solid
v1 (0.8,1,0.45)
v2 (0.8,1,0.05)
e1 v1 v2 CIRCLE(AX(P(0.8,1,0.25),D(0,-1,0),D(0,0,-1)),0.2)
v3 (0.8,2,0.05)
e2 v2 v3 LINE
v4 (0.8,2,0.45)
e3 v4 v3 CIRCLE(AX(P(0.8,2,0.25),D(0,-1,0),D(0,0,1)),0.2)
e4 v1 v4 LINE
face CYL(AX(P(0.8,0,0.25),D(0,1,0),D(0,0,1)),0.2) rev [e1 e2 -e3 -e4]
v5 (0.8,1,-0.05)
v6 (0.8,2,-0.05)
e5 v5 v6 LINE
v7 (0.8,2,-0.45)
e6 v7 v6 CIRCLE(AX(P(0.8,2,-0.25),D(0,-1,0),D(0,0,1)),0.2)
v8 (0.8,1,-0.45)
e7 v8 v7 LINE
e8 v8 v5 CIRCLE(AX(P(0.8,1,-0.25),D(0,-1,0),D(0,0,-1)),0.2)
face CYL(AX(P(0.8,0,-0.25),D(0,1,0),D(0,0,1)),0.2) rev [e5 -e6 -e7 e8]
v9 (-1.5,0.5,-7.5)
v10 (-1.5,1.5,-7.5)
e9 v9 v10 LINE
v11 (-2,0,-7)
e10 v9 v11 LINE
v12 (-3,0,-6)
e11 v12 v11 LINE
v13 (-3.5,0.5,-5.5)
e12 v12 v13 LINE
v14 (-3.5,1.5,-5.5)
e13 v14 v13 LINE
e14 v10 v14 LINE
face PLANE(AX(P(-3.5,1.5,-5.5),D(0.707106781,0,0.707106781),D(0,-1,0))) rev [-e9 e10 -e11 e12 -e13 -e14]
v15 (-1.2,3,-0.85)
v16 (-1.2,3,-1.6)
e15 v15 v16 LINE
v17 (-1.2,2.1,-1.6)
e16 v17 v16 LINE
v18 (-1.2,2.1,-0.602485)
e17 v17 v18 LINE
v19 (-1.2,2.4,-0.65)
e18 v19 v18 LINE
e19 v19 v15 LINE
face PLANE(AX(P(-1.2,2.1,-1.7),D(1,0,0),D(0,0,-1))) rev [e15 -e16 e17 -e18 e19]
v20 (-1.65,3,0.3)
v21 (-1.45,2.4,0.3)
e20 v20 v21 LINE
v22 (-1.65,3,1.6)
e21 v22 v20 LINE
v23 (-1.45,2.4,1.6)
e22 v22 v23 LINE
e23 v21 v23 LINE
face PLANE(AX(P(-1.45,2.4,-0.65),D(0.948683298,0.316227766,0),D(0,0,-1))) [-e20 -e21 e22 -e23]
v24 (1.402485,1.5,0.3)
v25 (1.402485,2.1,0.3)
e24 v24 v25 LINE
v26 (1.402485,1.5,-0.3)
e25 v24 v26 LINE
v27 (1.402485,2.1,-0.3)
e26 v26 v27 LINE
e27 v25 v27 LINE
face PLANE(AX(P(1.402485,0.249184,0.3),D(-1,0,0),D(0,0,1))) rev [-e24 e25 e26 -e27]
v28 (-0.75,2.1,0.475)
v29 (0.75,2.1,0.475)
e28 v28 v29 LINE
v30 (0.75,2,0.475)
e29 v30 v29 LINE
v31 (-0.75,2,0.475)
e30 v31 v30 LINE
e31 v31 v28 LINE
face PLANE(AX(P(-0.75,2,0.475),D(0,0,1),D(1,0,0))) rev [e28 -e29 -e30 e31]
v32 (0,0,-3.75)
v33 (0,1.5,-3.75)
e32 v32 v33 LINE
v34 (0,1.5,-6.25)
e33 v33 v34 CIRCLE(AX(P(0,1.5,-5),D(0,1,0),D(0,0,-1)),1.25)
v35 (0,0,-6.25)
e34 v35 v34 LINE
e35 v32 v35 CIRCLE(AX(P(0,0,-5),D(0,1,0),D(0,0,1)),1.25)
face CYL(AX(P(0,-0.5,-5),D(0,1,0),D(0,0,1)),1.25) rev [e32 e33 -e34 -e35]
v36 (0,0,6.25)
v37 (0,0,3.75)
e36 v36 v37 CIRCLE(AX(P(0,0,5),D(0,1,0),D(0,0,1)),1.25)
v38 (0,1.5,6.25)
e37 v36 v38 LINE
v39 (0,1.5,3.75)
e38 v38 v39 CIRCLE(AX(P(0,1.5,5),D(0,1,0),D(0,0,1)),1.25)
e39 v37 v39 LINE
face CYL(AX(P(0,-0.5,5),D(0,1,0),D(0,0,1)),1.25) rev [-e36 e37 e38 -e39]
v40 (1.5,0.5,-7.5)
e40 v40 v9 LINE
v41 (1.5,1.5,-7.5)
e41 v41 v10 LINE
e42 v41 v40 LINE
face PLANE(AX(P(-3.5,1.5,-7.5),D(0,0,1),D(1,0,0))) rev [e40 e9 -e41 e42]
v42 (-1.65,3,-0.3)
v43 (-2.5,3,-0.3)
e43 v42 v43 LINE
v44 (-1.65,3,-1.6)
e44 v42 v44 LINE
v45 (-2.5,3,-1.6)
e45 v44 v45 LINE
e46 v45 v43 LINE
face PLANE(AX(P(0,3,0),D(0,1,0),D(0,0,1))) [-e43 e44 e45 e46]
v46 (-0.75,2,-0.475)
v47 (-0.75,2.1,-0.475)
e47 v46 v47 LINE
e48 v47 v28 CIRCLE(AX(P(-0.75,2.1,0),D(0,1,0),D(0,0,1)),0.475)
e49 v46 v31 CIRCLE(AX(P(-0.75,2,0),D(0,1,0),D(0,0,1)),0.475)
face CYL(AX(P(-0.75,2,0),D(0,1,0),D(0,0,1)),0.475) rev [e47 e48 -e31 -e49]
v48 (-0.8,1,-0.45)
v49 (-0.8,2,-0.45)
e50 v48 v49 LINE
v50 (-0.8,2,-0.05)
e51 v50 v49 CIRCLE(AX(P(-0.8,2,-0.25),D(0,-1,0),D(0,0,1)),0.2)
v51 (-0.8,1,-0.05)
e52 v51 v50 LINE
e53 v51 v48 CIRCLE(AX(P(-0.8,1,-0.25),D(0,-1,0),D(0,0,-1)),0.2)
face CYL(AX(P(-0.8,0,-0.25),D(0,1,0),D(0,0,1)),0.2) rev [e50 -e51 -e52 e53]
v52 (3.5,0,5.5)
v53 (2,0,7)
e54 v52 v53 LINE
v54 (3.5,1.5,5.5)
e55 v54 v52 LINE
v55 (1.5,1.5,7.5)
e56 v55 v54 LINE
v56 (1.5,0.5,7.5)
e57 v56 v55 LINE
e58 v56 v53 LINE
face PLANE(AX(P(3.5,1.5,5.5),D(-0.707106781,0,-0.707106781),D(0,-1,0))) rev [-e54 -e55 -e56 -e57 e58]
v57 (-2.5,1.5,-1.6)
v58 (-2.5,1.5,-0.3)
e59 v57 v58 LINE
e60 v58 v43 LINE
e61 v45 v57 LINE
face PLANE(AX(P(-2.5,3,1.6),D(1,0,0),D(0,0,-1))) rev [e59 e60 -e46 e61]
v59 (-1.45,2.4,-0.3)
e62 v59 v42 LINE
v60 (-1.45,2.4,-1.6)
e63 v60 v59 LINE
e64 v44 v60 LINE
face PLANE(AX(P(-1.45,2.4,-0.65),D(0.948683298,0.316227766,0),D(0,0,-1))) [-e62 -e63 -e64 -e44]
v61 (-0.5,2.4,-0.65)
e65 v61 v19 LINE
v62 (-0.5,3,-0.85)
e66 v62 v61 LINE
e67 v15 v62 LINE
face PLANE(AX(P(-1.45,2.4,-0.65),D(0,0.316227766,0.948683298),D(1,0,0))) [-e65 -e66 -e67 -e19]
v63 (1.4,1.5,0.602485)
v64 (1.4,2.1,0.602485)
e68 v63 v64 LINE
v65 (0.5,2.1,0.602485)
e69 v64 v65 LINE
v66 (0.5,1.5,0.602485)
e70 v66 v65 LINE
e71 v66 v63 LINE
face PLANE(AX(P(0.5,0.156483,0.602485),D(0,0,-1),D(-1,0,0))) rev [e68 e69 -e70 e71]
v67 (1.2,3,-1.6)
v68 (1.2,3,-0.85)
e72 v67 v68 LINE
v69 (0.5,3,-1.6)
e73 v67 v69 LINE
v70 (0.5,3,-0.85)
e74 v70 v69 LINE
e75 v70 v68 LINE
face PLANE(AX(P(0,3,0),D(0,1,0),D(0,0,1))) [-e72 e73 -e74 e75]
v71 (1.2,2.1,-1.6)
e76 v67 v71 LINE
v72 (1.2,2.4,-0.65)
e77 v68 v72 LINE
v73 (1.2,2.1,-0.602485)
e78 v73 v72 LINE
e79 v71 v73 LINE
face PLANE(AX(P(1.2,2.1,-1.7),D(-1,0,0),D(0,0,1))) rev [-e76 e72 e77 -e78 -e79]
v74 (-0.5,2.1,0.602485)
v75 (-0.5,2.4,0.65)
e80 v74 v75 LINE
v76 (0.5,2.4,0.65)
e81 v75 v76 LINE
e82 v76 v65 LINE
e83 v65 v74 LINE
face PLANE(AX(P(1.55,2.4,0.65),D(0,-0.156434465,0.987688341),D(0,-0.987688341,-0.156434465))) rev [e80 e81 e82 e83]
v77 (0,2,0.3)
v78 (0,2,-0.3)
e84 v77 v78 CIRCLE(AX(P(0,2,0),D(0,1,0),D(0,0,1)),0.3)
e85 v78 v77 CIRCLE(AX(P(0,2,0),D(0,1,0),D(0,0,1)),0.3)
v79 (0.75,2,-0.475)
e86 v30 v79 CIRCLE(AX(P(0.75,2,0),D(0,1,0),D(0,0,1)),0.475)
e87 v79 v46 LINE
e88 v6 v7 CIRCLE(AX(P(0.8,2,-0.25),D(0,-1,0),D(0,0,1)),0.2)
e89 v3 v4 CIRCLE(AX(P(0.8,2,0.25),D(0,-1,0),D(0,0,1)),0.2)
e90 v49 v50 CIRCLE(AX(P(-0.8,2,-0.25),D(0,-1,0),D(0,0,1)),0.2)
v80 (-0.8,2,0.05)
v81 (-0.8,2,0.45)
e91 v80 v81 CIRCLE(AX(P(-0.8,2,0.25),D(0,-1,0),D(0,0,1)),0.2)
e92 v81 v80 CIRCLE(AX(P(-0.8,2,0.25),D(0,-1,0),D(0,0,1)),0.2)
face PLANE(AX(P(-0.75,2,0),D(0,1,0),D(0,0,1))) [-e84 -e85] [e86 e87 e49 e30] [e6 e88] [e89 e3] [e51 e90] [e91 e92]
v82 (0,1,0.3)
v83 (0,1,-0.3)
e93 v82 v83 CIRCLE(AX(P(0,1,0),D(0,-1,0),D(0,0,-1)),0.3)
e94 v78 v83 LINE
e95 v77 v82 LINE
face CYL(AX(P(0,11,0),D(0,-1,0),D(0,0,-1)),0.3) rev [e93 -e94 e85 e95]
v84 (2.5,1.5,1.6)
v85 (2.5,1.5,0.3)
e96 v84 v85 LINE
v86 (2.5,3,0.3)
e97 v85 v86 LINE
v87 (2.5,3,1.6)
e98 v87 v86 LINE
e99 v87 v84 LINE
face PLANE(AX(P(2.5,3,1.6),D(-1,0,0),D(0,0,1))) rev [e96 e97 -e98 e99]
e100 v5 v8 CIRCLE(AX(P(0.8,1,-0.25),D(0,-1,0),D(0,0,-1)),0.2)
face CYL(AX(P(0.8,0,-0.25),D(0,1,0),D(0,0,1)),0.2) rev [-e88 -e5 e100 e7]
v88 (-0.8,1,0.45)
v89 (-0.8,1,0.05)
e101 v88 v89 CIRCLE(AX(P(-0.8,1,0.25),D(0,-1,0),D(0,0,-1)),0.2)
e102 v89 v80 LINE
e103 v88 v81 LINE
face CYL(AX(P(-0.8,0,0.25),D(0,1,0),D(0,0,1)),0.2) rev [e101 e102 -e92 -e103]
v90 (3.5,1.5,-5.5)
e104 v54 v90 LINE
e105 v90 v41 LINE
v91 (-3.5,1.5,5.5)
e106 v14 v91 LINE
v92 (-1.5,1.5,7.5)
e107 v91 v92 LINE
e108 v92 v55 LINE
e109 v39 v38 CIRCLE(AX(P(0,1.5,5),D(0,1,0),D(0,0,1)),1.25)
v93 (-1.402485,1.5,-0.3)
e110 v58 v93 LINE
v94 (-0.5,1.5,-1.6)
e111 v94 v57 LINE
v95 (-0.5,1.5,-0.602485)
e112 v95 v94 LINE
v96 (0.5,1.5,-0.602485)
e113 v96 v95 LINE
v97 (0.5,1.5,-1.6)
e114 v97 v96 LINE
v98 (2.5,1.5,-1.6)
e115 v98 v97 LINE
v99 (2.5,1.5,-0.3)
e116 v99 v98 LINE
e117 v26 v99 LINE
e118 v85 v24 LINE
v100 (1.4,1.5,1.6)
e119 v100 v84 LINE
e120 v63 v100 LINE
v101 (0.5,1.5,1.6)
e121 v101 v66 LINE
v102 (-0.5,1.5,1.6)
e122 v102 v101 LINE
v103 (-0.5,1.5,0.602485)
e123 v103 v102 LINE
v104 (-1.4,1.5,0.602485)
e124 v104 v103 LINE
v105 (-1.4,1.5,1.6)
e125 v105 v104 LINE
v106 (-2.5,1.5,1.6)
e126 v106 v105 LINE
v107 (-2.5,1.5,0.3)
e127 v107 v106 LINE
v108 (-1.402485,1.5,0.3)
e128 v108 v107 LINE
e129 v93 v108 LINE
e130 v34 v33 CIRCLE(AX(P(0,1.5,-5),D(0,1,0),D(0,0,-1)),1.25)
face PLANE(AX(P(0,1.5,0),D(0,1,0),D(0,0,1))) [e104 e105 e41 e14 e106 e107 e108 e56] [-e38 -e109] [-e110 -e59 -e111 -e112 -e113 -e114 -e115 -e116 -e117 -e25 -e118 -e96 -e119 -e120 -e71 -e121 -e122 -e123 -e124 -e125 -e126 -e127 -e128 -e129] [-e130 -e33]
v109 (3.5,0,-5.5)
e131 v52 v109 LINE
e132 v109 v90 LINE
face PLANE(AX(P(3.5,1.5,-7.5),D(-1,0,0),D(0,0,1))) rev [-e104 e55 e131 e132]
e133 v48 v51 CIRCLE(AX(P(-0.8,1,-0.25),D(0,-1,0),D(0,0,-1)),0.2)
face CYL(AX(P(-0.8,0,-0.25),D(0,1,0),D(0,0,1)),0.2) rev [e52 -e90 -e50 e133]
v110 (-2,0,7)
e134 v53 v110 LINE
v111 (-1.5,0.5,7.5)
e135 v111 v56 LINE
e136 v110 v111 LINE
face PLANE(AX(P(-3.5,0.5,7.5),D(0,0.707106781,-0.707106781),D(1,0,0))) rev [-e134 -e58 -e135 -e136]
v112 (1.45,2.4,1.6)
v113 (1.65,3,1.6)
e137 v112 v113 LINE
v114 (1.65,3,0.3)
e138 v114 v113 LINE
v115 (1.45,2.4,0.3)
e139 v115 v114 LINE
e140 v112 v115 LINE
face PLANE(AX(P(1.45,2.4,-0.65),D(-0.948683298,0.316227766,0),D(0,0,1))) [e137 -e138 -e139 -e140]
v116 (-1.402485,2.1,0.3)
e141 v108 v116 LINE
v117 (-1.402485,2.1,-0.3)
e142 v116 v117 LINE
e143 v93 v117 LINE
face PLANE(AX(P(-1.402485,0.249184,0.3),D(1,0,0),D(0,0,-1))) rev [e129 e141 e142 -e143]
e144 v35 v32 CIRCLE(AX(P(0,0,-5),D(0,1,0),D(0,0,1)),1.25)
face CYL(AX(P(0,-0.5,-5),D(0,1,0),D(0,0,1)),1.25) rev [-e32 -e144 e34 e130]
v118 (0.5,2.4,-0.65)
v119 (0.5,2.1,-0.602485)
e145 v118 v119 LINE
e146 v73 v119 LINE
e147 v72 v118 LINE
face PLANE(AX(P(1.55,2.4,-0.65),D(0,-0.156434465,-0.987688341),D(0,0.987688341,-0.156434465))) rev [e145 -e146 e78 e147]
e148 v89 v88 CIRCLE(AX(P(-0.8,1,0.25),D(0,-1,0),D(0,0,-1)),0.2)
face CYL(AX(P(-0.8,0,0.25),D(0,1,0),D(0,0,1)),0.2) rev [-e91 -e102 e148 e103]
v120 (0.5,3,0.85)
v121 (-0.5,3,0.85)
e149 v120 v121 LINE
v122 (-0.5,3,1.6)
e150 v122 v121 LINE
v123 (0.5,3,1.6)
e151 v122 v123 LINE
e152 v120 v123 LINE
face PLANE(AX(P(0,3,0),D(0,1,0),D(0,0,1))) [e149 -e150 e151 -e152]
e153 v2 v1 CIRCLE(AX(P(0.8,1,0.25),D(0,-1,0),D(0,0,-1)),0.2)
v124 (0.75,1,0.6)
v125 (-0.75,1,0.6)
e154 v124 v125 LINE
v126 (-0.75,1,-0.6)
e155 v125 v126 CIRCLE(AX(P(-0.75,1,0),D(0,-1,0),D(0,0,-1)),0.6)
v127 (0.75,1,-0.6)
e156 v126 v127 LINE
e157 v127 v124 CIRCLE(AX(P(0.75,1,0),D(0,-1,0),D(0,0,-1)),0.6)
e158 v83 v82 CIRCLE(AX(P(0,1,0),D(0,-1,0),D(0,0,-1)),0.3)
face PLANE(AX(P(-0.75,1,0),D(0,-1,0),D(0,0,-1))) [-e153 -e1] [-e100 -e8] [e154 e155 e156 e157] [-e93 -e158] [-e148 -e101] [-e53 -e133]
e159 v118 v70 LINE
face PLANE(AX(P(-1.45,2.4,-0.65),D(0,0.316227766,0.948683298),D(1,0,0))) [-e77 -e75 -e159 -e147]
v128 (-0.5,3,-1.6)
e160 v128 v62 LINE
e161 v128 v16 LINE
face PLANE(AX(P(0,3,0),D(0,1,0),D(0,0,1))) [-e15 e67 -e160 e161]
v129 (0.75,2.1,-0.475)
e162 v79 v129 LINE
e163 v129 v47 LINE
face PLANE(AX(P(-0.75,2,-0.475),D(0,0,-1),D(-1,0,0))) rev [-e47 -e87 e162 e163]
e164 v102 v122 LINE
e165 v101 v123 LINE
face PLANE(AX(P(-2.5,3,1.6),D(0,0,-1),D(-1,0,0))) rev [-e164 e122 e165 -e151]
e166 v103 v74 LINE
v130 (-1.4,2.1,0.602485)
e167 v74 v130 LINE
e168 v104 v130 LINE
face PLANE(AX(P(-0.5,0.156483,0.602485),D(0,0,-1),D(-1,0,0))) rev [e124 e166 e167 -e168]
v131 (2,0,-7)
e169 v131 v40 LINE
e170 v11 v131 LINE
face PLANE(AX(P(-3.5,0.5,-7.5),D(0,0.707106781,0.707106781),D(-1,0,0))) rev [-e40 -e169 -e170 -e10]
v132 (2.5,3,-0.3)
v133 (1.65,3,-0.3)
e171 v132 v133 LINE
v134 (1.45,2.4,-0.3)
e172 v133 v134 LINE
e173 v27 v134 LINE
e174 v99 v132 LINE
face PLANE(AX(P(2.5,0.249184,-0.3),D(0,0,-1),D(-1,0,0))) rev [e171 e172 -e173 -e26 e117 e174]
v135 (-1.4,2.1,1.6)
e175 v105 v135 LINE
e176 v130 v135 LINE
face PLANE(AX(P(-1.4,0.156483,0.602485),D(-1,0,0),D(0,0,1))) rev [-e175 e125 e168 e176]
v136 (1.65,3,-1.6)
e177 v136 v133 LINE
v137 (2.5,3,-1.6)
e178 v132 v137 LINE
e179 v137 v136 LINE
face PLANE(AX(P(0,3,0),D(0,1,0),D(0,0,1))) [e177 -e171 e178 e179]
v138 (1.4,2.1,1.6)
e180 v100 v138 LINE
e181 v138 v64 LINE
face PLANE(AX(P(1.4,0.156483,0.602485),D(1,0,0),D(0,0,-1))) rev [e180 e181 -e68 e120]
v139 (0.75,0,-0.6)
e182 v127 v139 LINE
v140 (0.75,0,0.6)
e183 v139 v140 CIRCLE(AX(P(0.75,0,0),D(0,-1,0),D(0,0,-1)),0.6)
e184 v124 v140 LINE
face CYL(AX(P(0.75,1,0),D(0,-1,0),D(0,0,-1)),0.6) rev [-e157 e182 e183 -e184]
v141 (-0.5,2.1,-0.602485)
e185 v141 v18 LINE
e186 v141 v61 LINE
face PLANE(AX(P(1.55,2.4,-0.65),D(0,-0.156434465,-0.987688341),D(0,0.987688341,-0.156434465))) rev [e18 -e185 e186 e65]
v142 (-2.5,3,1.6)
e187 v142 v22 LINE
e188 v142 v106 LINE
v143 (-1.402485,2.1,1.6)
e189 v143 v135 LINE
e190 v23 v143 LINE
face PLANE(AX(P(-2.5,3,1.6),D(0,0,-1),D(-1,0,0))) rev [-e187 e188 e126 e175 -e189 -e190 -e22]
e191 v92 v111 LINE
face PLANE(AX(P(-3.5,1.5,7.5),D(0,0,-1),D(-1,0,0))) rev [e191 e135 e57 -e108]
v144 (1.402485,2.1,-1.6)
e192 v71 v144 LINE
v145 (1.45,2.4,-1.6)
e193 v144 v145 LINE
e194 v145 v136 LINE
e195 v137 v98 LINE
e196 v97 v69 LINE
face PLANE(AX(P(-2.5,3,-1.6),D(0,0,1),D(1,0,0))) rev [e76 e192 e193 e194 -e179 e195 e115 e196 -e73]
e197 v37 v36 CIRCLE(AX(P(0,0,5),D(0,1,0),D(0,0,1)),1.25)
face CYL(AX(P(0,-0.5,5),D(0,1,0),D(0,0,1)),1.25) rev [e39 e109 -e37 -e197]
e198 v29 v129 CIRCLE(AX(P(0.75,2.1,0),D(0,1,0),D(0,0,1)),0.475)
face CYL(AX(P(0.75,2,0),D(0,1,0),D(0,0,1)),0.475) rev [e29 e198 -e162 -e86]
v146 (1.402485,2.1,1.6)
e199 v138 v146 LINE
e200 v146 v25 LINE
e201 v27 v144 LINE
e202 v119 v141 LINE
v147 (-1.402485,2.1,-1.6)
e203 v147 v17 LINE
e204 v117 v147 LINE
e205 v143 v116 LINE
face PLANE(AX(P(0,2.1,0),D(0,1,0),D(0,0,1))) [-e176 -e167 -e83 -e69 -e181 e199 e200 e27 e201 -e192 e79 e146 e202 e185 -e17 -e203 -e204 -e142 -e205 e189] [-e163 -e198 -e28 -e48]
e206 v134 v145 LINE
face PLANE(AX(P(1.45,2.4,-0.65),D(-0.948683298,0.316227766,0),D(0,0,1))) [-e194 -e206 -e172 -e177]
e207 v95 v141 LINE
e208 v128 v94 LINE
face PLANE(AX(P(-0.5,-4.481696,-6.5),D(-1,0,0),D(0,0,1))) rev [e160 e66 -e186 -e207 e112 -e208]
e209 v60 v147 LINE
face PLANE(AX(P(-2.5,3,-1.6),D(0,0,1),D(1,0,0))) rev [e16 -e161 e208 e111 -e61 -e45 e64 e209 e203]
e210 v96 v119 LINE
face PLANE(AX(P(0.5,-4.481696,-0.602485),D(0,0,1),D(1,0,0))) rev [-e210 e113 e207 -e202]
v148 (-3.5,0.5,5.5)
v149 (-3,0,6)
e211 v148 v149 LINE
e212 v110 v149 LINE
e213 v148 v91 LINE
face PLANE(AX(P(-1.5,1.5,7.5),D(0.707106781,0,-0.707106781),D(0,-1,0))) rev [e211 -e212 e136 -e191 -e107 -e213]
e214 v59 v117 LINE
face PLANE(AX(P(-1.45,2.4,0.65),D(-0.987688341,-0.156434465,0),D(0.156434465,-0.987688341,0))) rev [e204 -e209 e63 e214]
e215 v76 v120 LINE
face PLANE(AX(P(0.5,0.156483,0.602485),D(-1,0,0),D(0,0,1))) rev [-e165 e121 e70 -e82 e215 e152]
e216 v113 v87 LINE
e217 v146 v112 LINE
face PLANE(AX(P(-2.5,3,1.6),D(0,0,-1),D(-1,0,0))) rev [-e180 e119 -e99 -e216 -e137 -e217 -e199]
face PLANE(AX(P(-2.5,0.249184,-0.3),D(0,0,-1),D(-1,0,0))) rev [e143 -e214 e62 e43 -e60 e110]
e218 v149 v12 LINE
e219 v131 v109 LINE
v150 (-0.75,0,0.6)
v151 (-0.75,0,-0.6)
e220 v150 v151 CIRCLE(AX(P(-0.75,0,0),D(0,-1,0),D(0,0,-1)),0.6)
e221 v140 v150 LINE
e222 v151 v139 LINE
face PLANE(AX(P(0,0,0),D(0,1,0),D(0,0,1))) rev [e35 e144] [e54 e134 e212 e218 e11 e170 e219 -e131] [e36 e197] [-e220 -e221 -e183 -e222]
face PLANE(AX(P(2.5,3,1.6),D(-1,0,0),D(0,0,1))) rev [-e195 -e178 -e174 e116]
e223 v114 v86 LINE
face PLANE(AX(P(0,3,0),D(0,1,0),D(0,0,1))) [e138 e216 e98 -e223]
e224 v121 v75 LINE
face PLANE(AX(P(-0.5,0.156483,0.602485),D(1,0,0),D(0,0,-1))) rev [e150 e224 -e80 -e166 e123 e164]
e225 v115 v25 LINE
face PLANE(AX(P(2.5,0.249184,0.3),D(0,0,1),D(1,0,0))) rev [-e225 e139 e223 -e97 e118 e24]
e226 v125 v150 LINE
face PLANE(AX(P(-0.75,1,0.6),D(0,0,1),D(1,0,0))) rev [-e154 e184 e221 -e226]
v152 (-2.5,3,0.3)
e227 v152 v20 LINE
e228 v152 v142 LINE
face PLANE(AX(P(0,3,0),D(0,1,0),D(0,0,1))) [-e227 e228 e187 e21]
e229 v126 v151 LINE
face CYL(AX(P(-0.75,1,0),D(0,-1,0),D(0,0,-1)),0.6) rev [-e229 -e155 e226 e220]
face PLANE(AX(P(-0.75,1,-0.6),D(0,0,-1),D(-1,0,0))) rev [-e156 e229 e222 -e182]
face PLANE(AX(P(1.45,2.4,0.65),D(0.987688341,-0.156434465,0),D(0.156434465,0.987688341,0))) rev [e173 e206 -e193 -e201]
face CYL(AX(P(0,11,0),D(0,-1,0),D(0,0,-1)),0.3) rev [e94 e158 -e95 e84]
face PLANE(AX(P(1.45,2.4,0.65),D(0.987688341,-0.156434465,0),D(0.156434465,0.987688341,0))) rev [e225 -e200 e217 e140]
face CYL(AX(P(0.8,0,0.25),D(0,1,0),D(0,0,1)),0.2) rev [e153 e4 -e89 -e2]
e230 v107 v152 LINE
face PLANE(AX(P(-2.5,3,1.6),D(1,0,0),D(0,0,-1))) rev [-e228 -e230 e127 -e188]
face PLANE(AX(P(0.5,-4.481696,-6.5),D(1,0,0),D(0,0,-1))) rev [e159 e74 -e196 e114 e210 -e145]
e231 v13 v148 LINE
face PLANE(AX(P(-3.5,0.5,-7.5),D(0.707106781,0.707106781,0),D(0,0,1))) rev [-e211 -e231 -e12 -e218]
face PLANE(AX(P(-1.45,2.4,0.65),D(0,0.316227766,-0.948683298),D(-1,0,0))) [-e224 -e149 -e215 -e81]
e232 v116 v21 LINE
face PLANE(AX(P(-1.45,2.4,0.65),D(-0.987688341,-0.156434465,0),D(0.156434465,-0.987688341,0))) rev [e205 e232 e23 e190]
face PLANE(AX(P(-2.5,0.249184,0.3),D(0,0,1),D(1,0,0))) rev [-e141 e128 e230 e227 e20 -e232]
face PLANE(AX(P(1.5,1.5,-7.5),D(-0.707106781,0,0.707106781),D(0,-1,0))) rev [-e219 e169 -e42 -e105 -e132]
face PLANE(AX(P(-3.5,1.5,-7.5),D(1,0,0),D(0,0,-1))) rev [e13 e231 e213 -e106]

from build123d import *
from OCP.BRepFilletAPI import BRepFilletAPI_MakeChamfer

# Parameters (mm, degrees)
SKETCH1_W           = 7
SKETCH1_H           = 15
BOSS_EXTRUDE1_DEPTH = 1.5
SKETCH2_W           = 5
SKETCH2_H           = 3.2
BOSS_EXTRUDE2_DEPTH = 1.5
SKETCH3_W           = 2.9
SKETCH3_H           = 1.3
CUT_EXTRUDE1_DEPTH  = 0.9
CUT_EXTRUDE2_DEPTH  = 1
CHAMFER1_SIZE       = 0.2
CHAMFER1_SIZE2      = 0.6
CHAMFER2_SIZE       = 0.2
CHAMFER2_SIZE2      = 0.6
CHAMFER3_SIZE       = 2
SKETCH8_R           = 1.25
CUT_EXTRUDE6_DEPTH  = 2
SKETCH9_R           = 0.2
CUT_EXTRUDE7_DEPTH  = 9.538735269
CUT_EXTRUDE8_DEPTH  = 0.1
BOSS_EXTRUDE3_DEPTH = 1.55
BOSS_EXTRUDE4_DEPTH = 0.65
CUT_EXTRUDE3_REACH  = 10.803
SKETCH5_W           = 1
SKETCH5_H           = 5.897515332
CUT_EXTRUDE4_REACH  = 10.803
SKETCH6_W           = 1.097515332
SKETCH6_H           = 0.6
CUT_EXTRUDE5_REACH  = 10.803
SKETCH7_W           = 0.9
SKETCH7_H           = 0.997515332
CHAMFER5_SIZE       = 0.25
CHAMFER5_SIZE2      = 0.6
CUT_EXTRUDE9_DEPTH  = 1.3
CUT_EXTRUDE10_DEPTH = 3.3
SKETCH19_R          = 0.3
CUT_EXTRUDE11_DEPTH = 10
CHAMFER6_SIZE       = 0.5


with BuildPart() as part:
    # Sketch1 → Boss-Extrude1 (new body)
    with BuildSketch(Plane(origin=(0, 0, 0), x_dir=(1, 0, 0), z_dir=(0, 1, 0))):
        Rectangle(SKETCH1_W, SKETCH1_H)
    extrude(amount=BOSS_EXTRUDE1_DEPTH)

    # Sketch2 → Boss-Extrude2 (add)
    with BuildSketch(Plane(origin=(0, 1.5, 0), x_dir=(1, 0, 0), z_dir=(0, 1, 0))):
        Rectangle(SKETCH2_W, SKETCH2_H)
    extrude(amount=BOSS_EXTRUDE2_DEPTH)

    # Sketch3 → Cut-Extrude1 (cut)
    with BuildSketch(Plane(origin=(0, 3, 0), x_dir=(1, 0, 0), z_dir=(0, 1, 0))):
        Rectangle(SKETCH3_W, SKETCH3_H)
    extrude(amount=-CUT_EXTRUDE1_DEPTH, mode=Mode.SUBTRACT)

    # Sketch4 → Cut-Extrude2 (cut)
    with BuildSketch(Plane.XZ):
        with BuildLine():
            Line((-0.75, 0.6), (0.75, 0.6))
            ThreePointArc((0.75, 0.6), (1.35, 0), (0.75, -0.6))
            Line((0.75, -0.6), (-0.75, -0.6))
            ThreePointArc((-0.75, -0.6), (-1.35, 0), (-0.75, 0.6))
        make_face()
    extrude(amount=-CUT_EXTRUDE2_DEPTH, mode=Mode.SUBTRACT)

    # Chamfer1
    chamfer1_edges = [part.edges().sort_by_distance(p)[0] for p in [
        (0, 3, -0.65),
        (0, 3, 0.65),
    ]]
    chamfer1_side = [part.faces().sort_by_distance(p)[0] for p in [
        (-2.440636712, 3, 0),
    ]]
    chamfer(chamfer1_edges, length=CHAMFER1_SIZE, length2=CHAMFER1_SIZE2, reference=chamfer1_side[0])

    # Chamfer2
    chamfer2_edges = [part.edges().sort_by_distance(p)[0] for p in [
        (-1.45, 3, 0),
        (1.45, 3, 0),
    ]]
    chamfer2_side = [part.faces().sort_by_distance(p)[0] for p in [
        (0, 3, -0.909363288),
    ]]
    chamfer(chamfer2_edges, length=CHAMFER2_SIZE, length2=CHAMFER2_SIZE2, reference=chamfer2_side[0])

    # Chamfer3
    chamfer3_edges = [part.edges().sort_by_distance(p)[0] for p in [
        (3.5, 0.75, 7.5),
        (-3.5, 0.75, 7.5),
        (-3.5, 0.75, -7.5),
        (3.5, 0.75, -7.5),
    ]]
    chamfer(chamfer3_edges, length=CHAMFER3_SIZE)

    # Sketch8 → Cut-Extrude6 (cut)
    with BuildSketch(Plane(origin=(0, 1.5, 0), x_dir=(1, 0, 0), z_dir=(0, 1, 0))):
        with Locations(Location((0, -5, 0), (0, 0, 270))):
            Circle(SKETCH8_R)
        with Locations(Location((0, 5, 0), (0, 0, 270))):
            Circle(SKETCH8_R)
    extrude(amount=-CUT_EXTRUDE6_DEPTH, mode=Mode.SUBTRACT)

    # Sketch9 → Cut-Extrude7 (cut, through all)
    with BuildSketch(Plane(origin=(0, 2.1, 0), x_dir=(1, 0, 0), z_dir=(0, 1, 0))):
        with Locations(Location((-0.8, 0.25, 0), (0, 0, 270))):
            Circle(SKETCH9_R)
        with Locations(Location((0.8, 0.25, 0), (0, 0, 90))):
            Circle(SKETCH9_R)
        with Locations(Location((0.8, -0.25, 0), (0, 0, 270))):
            Circle(SKETCH9_R)
        with Locations(Location((-0.8, -0.25, 0), (0, 0, 90))):
            Circle(SKETCH9_R)
    extrude(amount=-CUT_EXTRUDE7_DEPTH, mode=Mode.SUBTRACT)

    # Sketch10 → Cut-Extrude8 (cut)
    with BuildSketch(Plane(origin=(0, 2.1, 0), x_dir=(1, 0, 0), z_dir=(0, 1, 0))):
        with BuildLine():
            Line((-0.75, 0.475), (0.75, 0.475))
            ThreePointArc((0.75, 0.475), (1.225, 0), (0.75, -0.475))
            Line((0.75, -0.475), (-0.75, -0.475))
            ThreePointArc((-0.75, -0.475), (-1.225, 0), (-0.75, 0.475))
        make_face()
    extrude(amount=-CUT_EXTRUDE8_DEPTH, mode=Mode.SUBTRACT)

    # Sketch12 → Boss-Extrude3 (add, symmetric)
    with BuildSketch(Plane(origin=(0, 0, 0), x_dir=(0, 0, -1), z_dir=(1, 0, 0))):
        Polygon((-0.65, 2.4), (-0.602484668, 2.1), (-0.65, 2.1), align=None)
        Polygon((0.65, 2.1), (0.65, 2.4), (0.602484668, 2.1), align=None)
    extrude(amount=BOSS_EXTRUDE3_DEPTH, both=True)

    # Sketch15 → Boss-Extrude4 (add, symmetric)
    with BuildSketch(Plane.XY):
        Polygon((-1.45, 2.4), (-1.402484668, 2.1), (-1.45, 2.1), align=None)
        Polygon((1.45, 2.1), (1.45, 2.4), (1.402484668, 2.1), align=None)
    extrude(amount=BOSS_EXTRUDE4_DEPTH, both=True)

    # Cut-Extrude3: up to this face of the body (flat: up to its plane)
    cut_extrude3_end = Plane(part.part.faces().sort_by_distance((0, 1.5, -7.334470546))[0])
    # Sketch5 → Cut-Extrude3 (cut, up to the picked face)
    with BuildSketch(Plane(origin=(0, 3, 0), x_dir=(1, 0, 0), z_dir=(0, 1, 0)), mode=Mode.PRIVATE) as cut_extrude3_sk1:
        with Locations((0, 3.551242334)):
            Rectangle(SKETCH5_W, SKETCH5_H)
    cut_extrude3_tool1 = split(extrude(cut_extrude3_sk1.sketch, amount=-CUT_EXTRUDE3_REACH, mode=Mode.PRIVATE), bisect_by=cut_extrude3_end, keep=Keep.BOTH, mode=Mode.PRIVATE)
    add(cut_extrude3_tool1.solids().sort_by(Axis((0, 3, -3.551242), (0, -1, 0)))[0], mode=Mode.SUBTRACT)

    # Cut-Extrude4: up to this face of the body (flat: up to its plane)
    cut_extrude4_end = Plane(part.part.faces().sort_by_distance((0, 1.5, -7.334470546))[0])
    # Sketch6 → Cut-Extrude4 (cut, up to the picked face)
    with BuildSketch(Plane(origin=(0, 3, 0), x_dir=(1, 0, 0), z_dir=(0, 1, 0)), mode=Mode.PRIVATE) as cut_extrude4_sk1:
        with Locations((-1.951242334, 0)):
            Rectangle(SKETCH6_W, SKETCH6_H)
    cut_extrude4_tool1 = split(extrude(cut_extrude4_sk1.sketch, amount=-CUT_EXTRUDE4_REACH, mode=Mode.PRIVATE), bisect_by=cut_extrude4_end, keep=Keep.BOTH, mode=Mode.PRIVATE)
    # Sketch6 → Cut-Extrude4 (cut, up to the picked face)
    with BuildSketch(Plane(origin=(0, 3, 0), x_dir=(1, 0, 0), z_dir=(0, 1, 0)), mode=Mode.PRIVATE) as cut_extrude4_sk2:
        with Locations((1.951242334, 0)):
            Rectangle(SKETCH6_W, SKETCH6_H)
    cut_extrude4_tool2 = split(extrude(cut_extrude4_sk2.sketch, amount=-CUT_EXTRUDE4_REACH, mode=Mode.PRIVATE), bisect_by=cut_extrude4_end, keep=Keep.BOTH, mode=Mode.PRIVATE)
    add(cut_extrude4_tool1.solids().sort_by(Axis((-1.951242, 3, 0), (0, -1, 0)))[0], mode=Mode.SUBTRACT)
    add(cut_extrude4_tool2.solids().sort_by(Axis((1.951242, 3, 0), (0, -1, 0)))[0], mode=Mode.SUBTRACT)

    # Cut-Extrude5: up to this face of the body (flat: up to its plane)
    cut_extrude5_end = Plane(part.part.faces().sort_by_distance((0, 1.5, -7.334470546))[0])
    # Sketch7 → Cut-Extrude5 (cut, up to the picked face)
    with BuildSketch(Plane(origin=(0, 3, 0), x_dir=(1, 0, 0), z_dir=(0, 1, 0)), mode=Mode.PRIVATE) as cut_extrude5_sk1:
        with Locations((-0.95, -1.101242334)):
            Rectangle(SKETCH7_W, SKETCH7_H)
    cut_extrude5_tool1 = split(extrude(cut_extrude5_sk1.sketch, amount=-CUT_EXTRUDE5_REACH, mode=Mode.PRIVATE), bisect_by=cut_extrude5_end, keep=Keep.BOTH, mode=Mode.PRIVATE)
    # Sketch7 → Cut-Extrude5 (cut, up to the picked face)
    with BuildSketch(Plane(origin=(0, 3, 0), x_dir=(1, 0, 0), z_dir=(0, 1, 0)), mode=Mode.PRIVATE) as cut_extrude5_sk2:
        with Locations((0.95, -1.101242334)):
            Rectangle(SKETCH7_W, SKETCH7_H)
    cut_extrude5_tool2 = split(extrude(cut_extrude5_sk2.sketch, amount=-CUT_EXTRUDE5_REACH, mode=Mode.PRIVATE), bisect_by=cut_extrude5_end, keep=Keep.BOTH, mode=Mode.PRIVATE)
    add(cut_extrude5_tool1.solids().sort_by(Axis((-0.95, 3, 1.101242), (0, -1, 0)))[0], mode=Mode.SUBTRACT)
    add(cut_extrude5_tool2.solids().sort_by(Axis((0.95, 3, 1.101242), (0, -1, 0)))[0], mode=Mode.SUBTRACT)

    # Chamfer5: one chamfer whose edges measure the first distance from different faces: ONE call of the kernel's chamfer builder (chamfer() names one face for all edges)
    chamfer5_edges_1 = [part.edges().sort_by_distance(p)[0] for p in [
        (1.4, 3, 1.225),
    ]]
    chamfer5_side_1 = [part.faces().sort_by_distance(p)[0] for p in [
        (1.995212766, 3, 0.989893617),
    ]]
    chamfer5_edges_2 = [part.edges().sort_by_distance(p)[0] for p in [
        (-1.4, 3, 1.225),
    ]]
    chamfer5_side_2 = [part.faces().sort_by_distance(p)[0] for p in [
        (-1.995212766, 3, 0.989893617),
    ]]
    chamfer5 = BRepFilletAPI_MakeChamfer(part.part.solid().wrapped)
    for e in chamfer5_edges_1:
        chamfer5.Add(CHAMFER5_SIZE, CHAMFER5_SIZE2, e.wrapped, chamfer5_side_1[0].wrapped)  # the first distance lies on this face
    for e in chamfer5_edges_2:
        chamfer5.Add(CHAMFER5_SIZE, CHAMFER5_SIZE2, e.wrapped, chamfer5_side_2[0].wrapped)  # the first distance lies on this face
    add(Compound.cast(chamfer5.Shape()), mode=Mode.REPLACE)

    # Sketch16 → Cut-Extrude9 (cut)
    with BuildSketch(Plane.XY.offset(1.6)):
        Polygon((-1.45, 2.4), (-1.65, 3), (-1.4, 2.4), (-1.320280654, 2.4), (-1.320280654, 2.1), (-1.402484668, 2.1), align=None)
        Polygon((1.320280654, 2.4), (1.320280654, 2.1), (1.402484668, 2.1), (1.45, 2.4), (1.65, 3), (1.4, 2.4), align=None)
    extrude(amount=-CUT_EXTRUDE9_DEPTH, mode=Mode.SUBTRACT)

    # Sketch18 → Cut-Extrude10 (cut)
    with BuildSketch(Plane.XY.offset(1.6)):
        Polygon((-1.402484668, 2.1), (-1.2, 2.1), (-1.2, 3.166690018), (-1.705563339, 3.166690018), (-1.45, 2.4), align=None)
        Polygon((1.45, 2.4), (1.402484668, 2.1), (1.2, 2.1), (1.2, 3.166690018), (1.705563339, 3.166690018), align=None)
    extrude(amount=-CUT_EXTRUDE10_DEPTH, mode=Mode.SUBTRACT)

    # Sketch19 → Cut-Extrude11 (cut)
    with BuildSketch(Plane.XZ.offset(-1)):
        with Locations(Location((0, 0, 0), (0, 0, 270))):
            Circle(SKETCH19_R)
    extrude(amount=-CUT_EXTRUDE11_DEPTH, mode=Mode.SUBTRACT)

    # Chamfer6
    chamfer6_edges = [part.edges().sort_by_distance(p)[0] for p in [
        (0, 0, -7.5),
        (0, 0, 7.5),
        (-3.5, 0, 0),
    ]]
    chamfer(chamfer6_edges, length=CHAMFER6_SIZE)


solid = part.part
